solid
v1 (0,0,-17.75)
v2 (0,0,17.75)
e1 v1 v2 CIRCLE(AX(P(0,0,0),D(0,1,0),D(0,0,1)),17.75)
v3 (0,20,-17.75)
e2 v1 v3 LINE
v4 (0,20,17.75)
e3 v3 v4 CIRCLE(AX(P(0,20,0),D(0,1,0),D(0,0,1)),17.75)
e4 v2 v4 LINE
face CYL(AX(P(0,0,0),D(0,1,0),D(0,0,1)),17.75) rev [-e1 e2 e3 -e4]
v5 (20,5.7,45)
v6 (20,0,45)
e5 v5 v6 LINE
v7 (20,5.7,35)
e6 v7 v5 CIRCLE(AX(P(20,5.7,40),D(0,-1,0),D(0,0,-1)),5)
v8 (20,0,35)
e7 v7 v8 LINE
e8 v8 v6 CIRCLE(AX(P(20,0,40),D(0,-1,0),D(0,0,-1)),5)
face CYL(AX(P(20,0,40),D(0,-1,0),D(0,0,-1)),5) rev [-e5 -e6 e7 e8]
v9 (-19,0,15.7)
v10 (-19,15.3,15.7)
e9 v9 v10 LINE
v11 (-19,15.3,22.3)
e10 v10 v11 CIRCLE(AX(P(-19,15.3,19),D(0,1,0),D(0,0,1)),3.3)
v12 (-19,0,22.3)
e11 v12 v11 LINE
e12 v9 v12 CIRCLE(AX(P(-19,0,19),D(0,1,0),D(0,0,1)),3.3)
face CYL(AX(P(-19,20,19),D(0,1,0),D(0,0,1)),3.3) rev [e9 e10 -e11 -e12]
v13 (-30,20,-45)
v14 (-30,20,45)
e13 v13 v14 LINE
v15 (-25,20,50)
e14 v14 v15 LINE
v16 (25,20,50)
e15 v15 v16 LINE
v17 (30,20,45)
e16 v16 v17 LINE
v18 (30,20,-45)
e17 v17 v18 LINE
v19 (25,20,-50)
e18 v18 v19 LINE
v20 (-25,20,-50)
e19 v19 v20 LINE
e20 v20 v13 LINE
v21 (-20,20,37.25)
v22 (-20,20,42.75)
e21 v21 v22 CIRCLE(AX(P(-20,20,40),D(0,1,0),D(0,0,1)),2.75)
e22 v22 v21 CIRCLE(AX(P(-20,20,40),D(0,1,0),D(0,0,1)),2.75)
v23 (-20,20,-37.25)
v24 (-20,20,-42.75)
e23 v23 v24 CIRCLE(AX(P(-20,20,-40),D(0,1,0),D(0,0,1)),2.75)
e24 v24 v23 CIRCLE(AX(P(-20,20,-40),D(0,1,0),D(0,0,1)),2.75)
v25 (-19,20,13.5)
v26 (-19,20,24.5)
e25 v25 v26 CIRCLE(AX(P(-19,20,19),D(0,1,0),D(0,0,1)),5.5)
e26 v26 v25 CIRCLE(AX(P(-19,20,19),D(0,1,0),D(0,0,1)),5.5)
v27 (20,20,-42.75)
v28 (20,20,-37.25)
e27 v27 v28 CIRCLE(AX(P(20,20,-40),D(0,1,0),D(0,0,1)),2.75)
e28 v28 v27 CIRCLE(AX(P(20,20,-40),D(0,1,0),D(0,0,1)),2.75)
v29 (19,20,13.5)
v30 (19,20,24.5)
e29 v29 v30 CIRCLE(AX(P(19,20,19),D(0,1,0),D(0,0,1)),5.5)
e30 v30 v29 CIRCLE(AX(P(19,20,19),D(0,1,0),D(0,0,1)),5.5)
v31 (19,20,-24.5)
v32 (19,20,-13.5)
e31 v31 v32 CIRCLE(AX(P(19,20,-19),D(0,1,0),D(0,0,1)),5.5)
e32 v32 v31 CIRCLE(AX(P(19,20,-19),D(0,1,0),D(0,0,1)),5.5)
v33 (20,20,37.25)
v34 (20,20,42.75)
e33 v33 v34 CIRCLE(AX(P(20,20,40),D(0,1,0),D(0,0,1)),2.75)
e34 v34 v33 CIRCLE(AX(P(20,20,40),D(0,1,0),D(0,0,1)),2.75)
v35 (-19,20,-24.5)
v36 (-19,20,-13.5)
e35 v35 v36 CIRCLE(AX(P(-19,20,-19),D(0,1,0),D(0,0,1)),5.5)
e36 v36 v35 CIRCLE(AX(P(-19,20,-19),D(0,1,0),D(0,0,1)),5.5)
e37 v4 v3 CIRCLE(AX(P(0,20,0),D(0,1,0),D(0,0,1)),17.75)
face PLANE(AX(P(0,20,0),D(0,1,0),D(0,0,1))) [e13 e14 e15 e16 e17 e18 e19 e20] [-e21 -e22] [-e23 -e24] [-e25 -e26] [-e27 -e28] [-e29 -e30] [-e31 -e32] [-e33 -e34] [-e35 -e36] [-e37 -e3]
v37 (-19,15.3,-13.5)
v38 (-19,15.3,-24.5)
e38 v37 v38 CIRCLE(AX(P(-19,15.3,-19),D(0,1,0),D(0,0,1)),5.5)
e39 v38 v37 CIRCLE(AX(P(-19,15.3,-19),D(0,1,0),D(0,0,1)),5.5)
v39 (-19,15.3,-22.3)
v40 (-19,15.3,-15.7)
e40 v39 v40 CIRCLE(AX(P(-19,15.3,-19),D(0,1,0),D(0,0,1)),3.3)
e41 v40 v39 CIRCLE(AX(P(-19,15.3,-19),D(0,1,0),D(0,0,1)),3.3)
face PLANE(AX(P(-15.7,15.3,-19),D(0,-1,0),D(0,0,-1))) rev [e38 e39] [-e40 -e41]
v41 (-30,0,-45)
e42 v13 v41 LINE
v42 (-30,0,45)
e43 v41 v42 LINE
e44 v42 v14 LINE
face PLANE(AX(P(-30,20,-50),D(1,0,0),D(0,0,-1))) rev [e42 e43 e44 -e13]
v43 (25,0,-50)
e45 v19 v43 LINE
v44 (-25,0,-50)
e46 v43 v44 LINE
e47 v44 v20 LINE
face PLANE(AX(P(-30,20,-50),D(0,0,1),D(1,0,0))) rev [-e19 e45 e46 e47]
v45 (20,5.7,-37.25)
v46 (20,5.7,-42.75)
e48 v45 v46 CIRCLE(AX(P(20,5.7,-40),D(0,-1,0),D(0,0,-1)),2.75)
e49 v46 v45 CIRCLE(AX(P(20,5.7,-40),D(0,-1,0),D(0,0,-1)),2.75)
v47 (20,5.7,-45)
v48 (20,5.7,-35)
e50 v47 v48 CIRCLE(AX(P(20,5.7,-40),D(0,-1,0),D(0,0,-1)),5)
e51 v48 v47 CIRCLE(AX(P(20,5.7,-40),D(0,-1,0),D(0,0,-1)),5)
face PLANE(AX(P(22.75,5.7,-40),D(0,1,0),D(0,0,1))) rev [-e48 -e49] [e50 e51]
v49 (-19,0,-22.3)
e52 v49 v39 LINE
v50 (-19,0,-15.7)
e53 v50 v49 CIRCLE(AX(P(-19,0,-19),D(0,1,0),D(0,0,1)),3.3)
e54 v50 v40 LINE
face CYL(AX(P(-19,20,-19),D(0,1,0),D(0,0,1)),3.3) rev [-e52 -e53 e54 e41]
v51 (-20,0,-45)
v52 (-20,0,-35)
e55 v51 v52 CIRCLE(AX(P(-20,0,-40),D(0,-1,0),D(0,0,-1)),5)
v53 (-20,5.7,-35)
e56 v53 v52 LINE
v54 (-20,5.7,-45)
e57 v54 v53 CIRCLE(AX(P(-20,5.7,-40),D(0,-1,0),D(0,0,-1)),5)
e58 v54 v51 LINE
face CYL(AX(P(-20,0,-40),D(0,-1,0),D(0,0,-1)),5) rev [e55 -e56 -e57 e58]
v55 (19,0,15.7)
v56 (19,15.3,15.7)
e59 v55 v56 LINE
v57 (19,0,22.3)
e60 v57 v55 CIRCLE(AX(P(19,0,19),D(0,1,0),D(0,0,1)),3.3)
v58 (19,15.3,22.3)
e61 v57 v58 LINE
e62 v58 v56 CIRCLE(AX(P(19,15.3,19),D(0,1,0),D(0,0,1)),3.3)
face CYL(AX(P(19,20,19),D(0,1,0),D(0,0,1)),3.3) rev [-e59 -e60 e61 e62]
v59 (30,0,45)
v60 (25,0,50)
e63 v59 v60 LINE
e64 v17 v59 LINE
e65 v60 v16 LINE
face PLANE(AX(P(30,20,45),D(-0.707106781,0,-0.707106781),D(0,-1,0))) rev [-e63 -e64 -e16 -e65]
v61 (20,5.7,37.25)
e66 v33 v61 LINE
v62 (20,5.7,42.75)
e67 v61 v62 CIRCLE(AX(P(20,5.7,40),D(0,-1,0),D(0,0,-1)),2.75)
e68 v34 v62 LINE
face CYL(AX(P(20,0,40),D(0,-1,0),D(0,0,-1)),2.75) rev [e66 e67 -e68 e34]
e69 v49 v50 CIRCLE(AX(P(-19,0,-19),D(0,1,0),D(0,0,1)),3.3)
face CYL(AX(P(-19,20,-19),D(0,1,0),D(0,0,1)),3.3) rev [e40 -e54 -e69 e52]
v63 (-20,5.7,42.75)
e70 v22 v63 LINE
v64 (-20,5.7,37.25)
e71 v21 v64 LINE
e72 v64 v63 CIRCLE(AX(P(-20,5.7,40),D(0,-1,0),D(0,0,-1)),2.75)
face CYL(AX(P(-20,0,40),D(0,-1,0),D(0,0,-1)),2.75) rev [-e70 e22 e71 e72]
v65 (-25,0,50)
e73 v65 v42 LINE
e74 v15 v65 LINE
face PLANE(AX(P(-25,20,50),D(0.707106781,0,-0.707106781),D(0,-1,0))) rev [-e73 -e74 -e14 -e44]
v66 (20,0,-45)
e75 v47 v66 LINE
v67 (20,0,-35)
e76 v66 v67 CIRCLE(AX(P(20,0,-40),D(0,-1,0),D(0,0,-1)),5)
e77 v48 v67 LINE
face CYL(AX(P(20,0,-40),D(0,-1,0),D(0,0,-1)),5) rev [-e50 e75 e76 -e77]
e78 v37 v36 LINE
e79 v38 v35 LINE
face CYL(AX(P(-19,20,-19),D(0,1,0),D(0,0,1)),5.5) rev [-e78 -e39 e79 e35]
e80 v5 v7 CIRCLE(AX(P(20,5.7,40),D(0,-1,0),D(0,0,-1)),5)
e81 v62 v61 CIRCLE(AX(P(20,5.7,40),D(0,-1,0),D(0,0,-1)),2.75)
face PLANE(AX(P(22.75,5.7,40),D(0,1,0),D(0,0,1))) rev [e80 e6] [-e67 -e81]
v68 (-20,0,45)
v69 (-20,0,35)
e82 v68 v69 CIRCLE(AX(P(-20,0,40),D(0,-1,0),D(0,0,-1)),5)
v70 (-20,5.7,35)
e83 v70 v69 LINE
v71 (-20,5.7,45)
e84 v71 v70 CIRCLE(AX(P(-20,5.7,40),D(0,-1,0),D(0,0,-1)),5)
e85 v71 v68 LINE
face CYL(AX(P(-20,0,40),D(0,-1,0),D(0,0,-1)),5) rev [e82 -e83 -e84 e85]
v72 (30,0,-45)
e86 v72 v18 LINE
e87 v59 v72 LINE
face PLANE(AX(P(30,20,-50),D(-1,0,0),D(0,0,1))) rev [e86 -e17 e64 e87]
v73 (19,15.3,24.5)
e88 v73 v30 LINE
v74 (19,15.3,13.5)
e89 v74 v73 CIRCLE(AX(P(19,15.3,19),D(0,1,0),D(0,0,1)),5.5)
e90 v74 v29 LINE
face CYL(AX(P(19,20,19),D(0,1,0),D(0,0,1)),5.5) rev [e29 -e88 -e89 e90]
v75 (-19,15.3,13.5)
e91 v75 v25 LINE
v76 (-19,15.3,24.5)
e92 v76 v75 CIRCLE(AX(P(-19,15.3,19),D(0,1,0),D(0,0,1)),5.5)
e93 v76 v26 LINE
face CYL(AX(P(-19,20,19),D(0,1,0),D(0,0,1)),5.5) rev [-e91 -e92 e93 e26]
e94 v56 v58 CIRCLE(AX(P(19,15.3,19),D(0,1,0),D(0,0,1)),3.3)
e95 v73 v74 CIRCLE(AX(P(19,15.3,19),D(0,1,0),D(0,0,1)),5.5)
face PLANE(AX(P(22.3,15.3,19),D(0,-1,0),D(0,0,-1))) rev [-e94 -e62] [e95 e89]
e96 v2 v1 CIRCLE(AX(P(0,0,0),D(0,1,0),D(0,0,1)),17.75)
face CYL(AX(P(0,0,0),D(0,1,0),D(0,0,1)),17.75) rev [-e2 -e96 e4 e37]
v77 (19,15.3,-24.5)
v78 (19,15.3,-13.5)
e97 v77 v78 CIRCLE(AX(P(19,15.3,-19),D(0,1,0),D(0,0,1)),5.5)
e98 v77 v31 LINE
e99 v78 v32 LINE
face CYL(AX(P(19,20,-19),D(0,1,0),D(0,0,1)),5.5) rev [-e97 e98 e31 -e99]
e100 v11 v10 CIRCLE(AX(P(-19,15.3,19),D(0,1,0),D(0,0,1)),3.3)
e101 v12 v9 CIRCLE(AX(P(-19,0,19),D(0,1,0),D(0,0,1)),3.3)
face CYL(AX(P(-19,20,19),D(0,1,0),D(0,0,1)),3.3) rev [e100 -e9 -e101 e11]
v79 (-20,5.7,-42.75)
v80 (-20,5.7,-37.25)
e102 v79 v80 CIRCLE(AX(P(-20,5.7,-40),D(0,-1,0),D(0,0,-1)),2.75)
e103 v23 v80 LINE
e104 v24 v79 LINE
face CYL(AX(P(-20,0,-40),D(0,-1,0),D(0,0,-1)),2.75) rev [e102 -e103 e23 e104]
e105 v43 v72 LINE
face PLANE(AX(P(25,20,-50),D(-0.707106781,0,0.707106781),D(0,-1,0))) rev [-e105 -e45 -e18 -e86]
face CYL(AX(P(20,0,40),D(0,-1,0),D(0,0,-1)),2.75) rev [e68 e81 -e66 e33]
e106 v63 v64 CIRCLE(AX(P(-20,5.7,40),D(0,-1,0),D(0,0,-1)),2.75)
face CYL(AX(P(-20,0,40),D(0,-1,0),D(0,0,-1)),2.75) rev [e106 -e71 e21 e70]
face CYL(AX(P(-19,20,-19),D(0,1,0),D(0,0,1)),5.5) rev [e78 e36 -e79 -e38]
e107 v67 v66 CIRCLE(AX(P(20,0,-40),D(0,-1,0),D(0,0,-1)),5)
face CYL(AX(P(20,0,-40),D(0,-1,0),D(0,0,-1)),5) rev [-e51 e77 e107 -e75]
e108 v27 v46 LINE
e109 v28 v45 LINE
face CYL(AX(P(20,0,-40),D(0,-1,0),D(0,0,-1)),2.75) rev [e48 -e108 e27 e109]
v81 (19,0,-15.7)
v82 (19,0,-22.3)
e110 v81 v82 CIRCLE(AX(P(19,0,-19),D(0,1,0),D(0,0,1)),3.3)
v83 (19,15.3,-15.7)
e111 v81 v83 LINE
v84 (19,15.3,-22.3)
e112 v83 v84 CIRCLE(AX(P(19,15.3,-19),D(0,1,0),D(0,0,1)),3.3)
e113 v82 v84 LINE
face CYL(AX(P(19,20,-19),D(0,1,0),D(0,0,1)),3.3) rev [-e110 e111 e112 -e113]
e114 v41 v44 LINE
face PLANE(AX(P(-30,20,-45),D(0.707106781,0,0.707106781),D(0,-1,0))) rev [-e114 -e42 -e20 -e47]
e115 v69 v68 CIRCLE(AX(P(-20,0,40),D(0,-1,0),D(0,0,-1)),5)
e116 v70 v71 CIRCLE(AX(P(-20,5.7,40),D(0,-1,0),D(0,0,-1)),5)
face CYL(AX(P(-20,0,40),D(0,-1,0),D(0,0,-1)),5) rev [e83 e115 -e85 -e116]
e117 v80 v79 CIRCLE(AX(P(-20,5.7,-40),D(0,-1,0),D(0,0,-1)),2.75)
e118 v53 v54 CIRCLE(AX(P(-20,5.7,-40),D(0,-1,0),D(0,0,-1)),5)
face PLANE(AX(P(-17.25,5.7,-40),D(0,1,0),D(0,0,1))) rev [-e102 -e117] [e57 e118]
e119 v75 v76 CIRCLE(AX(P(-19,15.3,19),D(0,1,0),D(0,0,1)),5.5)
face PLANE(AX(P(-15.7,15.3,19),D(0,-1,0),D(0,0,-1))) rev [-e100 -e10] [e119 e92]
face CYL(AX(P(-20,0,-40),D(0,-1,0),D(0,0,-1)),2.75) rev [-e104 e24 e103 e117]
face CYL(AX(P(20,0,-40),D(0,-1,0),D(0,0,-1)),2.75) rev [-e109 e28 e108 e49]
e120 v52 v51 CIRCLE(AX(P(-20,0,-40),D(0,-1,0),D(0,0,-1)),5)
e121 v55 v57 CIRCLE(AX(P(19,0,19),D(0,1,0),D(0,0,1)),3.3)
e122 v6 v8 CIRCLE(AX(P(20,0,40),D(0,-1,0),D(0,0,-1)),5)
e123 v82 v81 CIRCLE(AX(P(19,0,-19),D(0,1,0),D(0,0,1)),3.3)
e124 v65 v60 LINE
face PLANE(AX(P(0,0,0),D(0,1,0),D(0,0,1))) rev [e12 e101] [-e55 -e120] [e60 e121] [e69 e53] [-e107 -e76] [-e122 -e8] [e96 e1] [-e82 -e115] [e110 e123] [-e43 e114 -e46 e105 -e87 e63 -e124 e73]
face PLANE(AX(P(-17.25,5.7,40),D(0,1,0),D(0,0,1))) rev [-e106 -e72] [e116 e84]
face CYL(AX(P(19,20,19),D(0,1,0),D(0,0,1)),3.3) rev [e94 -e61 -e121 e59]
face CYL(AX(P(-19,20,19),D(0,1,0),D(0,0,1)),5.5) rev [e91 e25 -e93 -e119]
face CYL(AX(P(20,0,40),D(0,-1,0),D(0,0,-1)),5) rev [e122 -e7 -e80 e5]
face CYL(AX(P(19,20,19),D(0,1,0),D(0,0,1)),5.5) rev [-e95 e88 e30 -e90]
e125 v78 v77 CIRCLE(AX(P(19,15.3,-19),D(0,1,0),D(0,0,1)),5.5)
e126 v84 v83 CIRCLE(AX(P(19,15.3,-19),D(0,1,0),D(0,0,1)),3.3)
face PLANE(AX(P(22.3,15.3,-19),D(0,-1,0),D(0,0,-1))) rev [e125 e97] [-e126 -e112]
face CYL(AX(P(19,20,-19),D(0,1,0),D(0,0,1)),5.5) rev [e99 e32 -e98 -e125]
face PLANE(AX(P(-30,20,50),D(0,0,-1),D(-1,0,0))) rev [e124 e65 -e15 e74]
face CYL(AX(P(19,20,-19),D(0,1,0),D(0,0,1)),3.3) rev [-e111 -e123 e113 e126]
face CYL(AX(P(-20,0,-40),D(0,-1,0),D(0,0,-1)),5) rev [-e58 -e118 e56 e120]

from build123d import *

# Parameters (mm, degrees)
SKETCH_1_W                  = 60
SKETCH_1_H                  = 100
EXTRUDE_1_DEPTH             = 20
SKETCH_2_R                  = 17.75
CUT_EXTRUDE_1_DEPTH         = 20
HOLE_WIZARD_1_D             = 6.6
HOLE_WIZARD_1_DEPTH         = 30
HOLE_WIZARD_1_CBORE_D       = 11
HOLE_WIZARD_1_CBORE_DEPTH   = 4.7
HOLE_WIZARD_1_TIP           = 1.982840043
CHAMFER_1_SIZE              = 5
HOLE_WIZARD_1_2_D           = 5.5
HOLE_WIZARD_1_2_DEPTH       = 30
HOLE_WIZARD_1_2_CBORE_D     = 10
HOLE_WIZARD_1_2_CBORE_DEPTH = 5.7
HOLE_WIZARD_1_2_TIP         = 1.652366702


with BuildPart() as part:
    # 草图1 → 凸台-拉伸1 (new body)
    with BuildSketch(Plane(origin=(0, 0, 0), x_dir=(1, 0, 0), z_dir=(0, 1, 0))):
        Rectangle(SKETCH_1_W, SKETCH_1_H)
    extrude(amount=EXTRUDE_1_DEPTH)

    # 草图2 → 切除-拉伸1 (cut)
    with BuildSketch(Plane(origin=(0, 20, 0), x_dir=(1, 0, 0), z_dir=(0, 1, 0))):
        with Locations(Location((0, 0, 0), (0, 0, 270))):
            Circle(SKETCH_2_R)
    extrude(amount=-CUT_EXTRUDE_1_DEPTH, mode=Mode.SUBTRACT)

    # Hole Wizard 1
    with Locations(Plane(origin=(0, 20, 0), x_dir=(1, 0, 0), z_dir=(0, 1, 0))):
        with Locations((19, 19), (19, -19), (-19, 19), (-19, -19)):
            CounterBoreHole(HOLE_WIZARD_1_D / 2, HOLE_WIZARD_1_CBORE_D / 2, HOLE_WIZARD_1_CBORE_DEPTH, depth=HOLE_WIZARD_1_DEPTH)
            with Locations((0, 0, -(HOLE_WIZARD_1_DEPTH + HOLE_WIZARD_1_TIP / 2))):  # 118° drill point
                Cone(0, HOLE_WIZARD_1_D / 2, HOLE_WIZARD_1_TIP, mode=Mode.SUBTRACT)

    # 倒角1
    chamfer_1_edges = [part.edges().sort_by_distance(p)[0] for p in [
        (30, 10, 50),
        (-30, 10, 50),
        (-30, 10, -50),
        (30, 10, -50),
    ]]
    chamfer(chamfer_1_edges, length=CHAMFER_1_SIZE)

    # Hole Wizard 1 2
    with Locations(Plane(origin=(0, 0, 0), x_dir=(-1, 0, 0), z_dir=(0, -1, 0))):
        with Locations((20, 40), (-20, 40), (20, -40), (-20, -40)):
            CounterBoreHole(HOLE_WIZARD_1_2_D / 2, HOLE_WIZARD_1_2_CBORE_D / 2, HOLE_WIZARD_1_2_CBORE_DEPTH, depth=HOLE_WIZARD_1_2_DEPTH)
            with Locations((0, 0, -(HOLE_WIZARD_1_2_DEPTH + HOLE_WIZARD_1_2_TIP / 2))):  # 118° drill point
                Cone(0, HOLE_WIZARD_1_2_D / 2, HOLE_WIZARD_1_2_TIP, mode=Mode.SUBTRACT)


solid = part.part
